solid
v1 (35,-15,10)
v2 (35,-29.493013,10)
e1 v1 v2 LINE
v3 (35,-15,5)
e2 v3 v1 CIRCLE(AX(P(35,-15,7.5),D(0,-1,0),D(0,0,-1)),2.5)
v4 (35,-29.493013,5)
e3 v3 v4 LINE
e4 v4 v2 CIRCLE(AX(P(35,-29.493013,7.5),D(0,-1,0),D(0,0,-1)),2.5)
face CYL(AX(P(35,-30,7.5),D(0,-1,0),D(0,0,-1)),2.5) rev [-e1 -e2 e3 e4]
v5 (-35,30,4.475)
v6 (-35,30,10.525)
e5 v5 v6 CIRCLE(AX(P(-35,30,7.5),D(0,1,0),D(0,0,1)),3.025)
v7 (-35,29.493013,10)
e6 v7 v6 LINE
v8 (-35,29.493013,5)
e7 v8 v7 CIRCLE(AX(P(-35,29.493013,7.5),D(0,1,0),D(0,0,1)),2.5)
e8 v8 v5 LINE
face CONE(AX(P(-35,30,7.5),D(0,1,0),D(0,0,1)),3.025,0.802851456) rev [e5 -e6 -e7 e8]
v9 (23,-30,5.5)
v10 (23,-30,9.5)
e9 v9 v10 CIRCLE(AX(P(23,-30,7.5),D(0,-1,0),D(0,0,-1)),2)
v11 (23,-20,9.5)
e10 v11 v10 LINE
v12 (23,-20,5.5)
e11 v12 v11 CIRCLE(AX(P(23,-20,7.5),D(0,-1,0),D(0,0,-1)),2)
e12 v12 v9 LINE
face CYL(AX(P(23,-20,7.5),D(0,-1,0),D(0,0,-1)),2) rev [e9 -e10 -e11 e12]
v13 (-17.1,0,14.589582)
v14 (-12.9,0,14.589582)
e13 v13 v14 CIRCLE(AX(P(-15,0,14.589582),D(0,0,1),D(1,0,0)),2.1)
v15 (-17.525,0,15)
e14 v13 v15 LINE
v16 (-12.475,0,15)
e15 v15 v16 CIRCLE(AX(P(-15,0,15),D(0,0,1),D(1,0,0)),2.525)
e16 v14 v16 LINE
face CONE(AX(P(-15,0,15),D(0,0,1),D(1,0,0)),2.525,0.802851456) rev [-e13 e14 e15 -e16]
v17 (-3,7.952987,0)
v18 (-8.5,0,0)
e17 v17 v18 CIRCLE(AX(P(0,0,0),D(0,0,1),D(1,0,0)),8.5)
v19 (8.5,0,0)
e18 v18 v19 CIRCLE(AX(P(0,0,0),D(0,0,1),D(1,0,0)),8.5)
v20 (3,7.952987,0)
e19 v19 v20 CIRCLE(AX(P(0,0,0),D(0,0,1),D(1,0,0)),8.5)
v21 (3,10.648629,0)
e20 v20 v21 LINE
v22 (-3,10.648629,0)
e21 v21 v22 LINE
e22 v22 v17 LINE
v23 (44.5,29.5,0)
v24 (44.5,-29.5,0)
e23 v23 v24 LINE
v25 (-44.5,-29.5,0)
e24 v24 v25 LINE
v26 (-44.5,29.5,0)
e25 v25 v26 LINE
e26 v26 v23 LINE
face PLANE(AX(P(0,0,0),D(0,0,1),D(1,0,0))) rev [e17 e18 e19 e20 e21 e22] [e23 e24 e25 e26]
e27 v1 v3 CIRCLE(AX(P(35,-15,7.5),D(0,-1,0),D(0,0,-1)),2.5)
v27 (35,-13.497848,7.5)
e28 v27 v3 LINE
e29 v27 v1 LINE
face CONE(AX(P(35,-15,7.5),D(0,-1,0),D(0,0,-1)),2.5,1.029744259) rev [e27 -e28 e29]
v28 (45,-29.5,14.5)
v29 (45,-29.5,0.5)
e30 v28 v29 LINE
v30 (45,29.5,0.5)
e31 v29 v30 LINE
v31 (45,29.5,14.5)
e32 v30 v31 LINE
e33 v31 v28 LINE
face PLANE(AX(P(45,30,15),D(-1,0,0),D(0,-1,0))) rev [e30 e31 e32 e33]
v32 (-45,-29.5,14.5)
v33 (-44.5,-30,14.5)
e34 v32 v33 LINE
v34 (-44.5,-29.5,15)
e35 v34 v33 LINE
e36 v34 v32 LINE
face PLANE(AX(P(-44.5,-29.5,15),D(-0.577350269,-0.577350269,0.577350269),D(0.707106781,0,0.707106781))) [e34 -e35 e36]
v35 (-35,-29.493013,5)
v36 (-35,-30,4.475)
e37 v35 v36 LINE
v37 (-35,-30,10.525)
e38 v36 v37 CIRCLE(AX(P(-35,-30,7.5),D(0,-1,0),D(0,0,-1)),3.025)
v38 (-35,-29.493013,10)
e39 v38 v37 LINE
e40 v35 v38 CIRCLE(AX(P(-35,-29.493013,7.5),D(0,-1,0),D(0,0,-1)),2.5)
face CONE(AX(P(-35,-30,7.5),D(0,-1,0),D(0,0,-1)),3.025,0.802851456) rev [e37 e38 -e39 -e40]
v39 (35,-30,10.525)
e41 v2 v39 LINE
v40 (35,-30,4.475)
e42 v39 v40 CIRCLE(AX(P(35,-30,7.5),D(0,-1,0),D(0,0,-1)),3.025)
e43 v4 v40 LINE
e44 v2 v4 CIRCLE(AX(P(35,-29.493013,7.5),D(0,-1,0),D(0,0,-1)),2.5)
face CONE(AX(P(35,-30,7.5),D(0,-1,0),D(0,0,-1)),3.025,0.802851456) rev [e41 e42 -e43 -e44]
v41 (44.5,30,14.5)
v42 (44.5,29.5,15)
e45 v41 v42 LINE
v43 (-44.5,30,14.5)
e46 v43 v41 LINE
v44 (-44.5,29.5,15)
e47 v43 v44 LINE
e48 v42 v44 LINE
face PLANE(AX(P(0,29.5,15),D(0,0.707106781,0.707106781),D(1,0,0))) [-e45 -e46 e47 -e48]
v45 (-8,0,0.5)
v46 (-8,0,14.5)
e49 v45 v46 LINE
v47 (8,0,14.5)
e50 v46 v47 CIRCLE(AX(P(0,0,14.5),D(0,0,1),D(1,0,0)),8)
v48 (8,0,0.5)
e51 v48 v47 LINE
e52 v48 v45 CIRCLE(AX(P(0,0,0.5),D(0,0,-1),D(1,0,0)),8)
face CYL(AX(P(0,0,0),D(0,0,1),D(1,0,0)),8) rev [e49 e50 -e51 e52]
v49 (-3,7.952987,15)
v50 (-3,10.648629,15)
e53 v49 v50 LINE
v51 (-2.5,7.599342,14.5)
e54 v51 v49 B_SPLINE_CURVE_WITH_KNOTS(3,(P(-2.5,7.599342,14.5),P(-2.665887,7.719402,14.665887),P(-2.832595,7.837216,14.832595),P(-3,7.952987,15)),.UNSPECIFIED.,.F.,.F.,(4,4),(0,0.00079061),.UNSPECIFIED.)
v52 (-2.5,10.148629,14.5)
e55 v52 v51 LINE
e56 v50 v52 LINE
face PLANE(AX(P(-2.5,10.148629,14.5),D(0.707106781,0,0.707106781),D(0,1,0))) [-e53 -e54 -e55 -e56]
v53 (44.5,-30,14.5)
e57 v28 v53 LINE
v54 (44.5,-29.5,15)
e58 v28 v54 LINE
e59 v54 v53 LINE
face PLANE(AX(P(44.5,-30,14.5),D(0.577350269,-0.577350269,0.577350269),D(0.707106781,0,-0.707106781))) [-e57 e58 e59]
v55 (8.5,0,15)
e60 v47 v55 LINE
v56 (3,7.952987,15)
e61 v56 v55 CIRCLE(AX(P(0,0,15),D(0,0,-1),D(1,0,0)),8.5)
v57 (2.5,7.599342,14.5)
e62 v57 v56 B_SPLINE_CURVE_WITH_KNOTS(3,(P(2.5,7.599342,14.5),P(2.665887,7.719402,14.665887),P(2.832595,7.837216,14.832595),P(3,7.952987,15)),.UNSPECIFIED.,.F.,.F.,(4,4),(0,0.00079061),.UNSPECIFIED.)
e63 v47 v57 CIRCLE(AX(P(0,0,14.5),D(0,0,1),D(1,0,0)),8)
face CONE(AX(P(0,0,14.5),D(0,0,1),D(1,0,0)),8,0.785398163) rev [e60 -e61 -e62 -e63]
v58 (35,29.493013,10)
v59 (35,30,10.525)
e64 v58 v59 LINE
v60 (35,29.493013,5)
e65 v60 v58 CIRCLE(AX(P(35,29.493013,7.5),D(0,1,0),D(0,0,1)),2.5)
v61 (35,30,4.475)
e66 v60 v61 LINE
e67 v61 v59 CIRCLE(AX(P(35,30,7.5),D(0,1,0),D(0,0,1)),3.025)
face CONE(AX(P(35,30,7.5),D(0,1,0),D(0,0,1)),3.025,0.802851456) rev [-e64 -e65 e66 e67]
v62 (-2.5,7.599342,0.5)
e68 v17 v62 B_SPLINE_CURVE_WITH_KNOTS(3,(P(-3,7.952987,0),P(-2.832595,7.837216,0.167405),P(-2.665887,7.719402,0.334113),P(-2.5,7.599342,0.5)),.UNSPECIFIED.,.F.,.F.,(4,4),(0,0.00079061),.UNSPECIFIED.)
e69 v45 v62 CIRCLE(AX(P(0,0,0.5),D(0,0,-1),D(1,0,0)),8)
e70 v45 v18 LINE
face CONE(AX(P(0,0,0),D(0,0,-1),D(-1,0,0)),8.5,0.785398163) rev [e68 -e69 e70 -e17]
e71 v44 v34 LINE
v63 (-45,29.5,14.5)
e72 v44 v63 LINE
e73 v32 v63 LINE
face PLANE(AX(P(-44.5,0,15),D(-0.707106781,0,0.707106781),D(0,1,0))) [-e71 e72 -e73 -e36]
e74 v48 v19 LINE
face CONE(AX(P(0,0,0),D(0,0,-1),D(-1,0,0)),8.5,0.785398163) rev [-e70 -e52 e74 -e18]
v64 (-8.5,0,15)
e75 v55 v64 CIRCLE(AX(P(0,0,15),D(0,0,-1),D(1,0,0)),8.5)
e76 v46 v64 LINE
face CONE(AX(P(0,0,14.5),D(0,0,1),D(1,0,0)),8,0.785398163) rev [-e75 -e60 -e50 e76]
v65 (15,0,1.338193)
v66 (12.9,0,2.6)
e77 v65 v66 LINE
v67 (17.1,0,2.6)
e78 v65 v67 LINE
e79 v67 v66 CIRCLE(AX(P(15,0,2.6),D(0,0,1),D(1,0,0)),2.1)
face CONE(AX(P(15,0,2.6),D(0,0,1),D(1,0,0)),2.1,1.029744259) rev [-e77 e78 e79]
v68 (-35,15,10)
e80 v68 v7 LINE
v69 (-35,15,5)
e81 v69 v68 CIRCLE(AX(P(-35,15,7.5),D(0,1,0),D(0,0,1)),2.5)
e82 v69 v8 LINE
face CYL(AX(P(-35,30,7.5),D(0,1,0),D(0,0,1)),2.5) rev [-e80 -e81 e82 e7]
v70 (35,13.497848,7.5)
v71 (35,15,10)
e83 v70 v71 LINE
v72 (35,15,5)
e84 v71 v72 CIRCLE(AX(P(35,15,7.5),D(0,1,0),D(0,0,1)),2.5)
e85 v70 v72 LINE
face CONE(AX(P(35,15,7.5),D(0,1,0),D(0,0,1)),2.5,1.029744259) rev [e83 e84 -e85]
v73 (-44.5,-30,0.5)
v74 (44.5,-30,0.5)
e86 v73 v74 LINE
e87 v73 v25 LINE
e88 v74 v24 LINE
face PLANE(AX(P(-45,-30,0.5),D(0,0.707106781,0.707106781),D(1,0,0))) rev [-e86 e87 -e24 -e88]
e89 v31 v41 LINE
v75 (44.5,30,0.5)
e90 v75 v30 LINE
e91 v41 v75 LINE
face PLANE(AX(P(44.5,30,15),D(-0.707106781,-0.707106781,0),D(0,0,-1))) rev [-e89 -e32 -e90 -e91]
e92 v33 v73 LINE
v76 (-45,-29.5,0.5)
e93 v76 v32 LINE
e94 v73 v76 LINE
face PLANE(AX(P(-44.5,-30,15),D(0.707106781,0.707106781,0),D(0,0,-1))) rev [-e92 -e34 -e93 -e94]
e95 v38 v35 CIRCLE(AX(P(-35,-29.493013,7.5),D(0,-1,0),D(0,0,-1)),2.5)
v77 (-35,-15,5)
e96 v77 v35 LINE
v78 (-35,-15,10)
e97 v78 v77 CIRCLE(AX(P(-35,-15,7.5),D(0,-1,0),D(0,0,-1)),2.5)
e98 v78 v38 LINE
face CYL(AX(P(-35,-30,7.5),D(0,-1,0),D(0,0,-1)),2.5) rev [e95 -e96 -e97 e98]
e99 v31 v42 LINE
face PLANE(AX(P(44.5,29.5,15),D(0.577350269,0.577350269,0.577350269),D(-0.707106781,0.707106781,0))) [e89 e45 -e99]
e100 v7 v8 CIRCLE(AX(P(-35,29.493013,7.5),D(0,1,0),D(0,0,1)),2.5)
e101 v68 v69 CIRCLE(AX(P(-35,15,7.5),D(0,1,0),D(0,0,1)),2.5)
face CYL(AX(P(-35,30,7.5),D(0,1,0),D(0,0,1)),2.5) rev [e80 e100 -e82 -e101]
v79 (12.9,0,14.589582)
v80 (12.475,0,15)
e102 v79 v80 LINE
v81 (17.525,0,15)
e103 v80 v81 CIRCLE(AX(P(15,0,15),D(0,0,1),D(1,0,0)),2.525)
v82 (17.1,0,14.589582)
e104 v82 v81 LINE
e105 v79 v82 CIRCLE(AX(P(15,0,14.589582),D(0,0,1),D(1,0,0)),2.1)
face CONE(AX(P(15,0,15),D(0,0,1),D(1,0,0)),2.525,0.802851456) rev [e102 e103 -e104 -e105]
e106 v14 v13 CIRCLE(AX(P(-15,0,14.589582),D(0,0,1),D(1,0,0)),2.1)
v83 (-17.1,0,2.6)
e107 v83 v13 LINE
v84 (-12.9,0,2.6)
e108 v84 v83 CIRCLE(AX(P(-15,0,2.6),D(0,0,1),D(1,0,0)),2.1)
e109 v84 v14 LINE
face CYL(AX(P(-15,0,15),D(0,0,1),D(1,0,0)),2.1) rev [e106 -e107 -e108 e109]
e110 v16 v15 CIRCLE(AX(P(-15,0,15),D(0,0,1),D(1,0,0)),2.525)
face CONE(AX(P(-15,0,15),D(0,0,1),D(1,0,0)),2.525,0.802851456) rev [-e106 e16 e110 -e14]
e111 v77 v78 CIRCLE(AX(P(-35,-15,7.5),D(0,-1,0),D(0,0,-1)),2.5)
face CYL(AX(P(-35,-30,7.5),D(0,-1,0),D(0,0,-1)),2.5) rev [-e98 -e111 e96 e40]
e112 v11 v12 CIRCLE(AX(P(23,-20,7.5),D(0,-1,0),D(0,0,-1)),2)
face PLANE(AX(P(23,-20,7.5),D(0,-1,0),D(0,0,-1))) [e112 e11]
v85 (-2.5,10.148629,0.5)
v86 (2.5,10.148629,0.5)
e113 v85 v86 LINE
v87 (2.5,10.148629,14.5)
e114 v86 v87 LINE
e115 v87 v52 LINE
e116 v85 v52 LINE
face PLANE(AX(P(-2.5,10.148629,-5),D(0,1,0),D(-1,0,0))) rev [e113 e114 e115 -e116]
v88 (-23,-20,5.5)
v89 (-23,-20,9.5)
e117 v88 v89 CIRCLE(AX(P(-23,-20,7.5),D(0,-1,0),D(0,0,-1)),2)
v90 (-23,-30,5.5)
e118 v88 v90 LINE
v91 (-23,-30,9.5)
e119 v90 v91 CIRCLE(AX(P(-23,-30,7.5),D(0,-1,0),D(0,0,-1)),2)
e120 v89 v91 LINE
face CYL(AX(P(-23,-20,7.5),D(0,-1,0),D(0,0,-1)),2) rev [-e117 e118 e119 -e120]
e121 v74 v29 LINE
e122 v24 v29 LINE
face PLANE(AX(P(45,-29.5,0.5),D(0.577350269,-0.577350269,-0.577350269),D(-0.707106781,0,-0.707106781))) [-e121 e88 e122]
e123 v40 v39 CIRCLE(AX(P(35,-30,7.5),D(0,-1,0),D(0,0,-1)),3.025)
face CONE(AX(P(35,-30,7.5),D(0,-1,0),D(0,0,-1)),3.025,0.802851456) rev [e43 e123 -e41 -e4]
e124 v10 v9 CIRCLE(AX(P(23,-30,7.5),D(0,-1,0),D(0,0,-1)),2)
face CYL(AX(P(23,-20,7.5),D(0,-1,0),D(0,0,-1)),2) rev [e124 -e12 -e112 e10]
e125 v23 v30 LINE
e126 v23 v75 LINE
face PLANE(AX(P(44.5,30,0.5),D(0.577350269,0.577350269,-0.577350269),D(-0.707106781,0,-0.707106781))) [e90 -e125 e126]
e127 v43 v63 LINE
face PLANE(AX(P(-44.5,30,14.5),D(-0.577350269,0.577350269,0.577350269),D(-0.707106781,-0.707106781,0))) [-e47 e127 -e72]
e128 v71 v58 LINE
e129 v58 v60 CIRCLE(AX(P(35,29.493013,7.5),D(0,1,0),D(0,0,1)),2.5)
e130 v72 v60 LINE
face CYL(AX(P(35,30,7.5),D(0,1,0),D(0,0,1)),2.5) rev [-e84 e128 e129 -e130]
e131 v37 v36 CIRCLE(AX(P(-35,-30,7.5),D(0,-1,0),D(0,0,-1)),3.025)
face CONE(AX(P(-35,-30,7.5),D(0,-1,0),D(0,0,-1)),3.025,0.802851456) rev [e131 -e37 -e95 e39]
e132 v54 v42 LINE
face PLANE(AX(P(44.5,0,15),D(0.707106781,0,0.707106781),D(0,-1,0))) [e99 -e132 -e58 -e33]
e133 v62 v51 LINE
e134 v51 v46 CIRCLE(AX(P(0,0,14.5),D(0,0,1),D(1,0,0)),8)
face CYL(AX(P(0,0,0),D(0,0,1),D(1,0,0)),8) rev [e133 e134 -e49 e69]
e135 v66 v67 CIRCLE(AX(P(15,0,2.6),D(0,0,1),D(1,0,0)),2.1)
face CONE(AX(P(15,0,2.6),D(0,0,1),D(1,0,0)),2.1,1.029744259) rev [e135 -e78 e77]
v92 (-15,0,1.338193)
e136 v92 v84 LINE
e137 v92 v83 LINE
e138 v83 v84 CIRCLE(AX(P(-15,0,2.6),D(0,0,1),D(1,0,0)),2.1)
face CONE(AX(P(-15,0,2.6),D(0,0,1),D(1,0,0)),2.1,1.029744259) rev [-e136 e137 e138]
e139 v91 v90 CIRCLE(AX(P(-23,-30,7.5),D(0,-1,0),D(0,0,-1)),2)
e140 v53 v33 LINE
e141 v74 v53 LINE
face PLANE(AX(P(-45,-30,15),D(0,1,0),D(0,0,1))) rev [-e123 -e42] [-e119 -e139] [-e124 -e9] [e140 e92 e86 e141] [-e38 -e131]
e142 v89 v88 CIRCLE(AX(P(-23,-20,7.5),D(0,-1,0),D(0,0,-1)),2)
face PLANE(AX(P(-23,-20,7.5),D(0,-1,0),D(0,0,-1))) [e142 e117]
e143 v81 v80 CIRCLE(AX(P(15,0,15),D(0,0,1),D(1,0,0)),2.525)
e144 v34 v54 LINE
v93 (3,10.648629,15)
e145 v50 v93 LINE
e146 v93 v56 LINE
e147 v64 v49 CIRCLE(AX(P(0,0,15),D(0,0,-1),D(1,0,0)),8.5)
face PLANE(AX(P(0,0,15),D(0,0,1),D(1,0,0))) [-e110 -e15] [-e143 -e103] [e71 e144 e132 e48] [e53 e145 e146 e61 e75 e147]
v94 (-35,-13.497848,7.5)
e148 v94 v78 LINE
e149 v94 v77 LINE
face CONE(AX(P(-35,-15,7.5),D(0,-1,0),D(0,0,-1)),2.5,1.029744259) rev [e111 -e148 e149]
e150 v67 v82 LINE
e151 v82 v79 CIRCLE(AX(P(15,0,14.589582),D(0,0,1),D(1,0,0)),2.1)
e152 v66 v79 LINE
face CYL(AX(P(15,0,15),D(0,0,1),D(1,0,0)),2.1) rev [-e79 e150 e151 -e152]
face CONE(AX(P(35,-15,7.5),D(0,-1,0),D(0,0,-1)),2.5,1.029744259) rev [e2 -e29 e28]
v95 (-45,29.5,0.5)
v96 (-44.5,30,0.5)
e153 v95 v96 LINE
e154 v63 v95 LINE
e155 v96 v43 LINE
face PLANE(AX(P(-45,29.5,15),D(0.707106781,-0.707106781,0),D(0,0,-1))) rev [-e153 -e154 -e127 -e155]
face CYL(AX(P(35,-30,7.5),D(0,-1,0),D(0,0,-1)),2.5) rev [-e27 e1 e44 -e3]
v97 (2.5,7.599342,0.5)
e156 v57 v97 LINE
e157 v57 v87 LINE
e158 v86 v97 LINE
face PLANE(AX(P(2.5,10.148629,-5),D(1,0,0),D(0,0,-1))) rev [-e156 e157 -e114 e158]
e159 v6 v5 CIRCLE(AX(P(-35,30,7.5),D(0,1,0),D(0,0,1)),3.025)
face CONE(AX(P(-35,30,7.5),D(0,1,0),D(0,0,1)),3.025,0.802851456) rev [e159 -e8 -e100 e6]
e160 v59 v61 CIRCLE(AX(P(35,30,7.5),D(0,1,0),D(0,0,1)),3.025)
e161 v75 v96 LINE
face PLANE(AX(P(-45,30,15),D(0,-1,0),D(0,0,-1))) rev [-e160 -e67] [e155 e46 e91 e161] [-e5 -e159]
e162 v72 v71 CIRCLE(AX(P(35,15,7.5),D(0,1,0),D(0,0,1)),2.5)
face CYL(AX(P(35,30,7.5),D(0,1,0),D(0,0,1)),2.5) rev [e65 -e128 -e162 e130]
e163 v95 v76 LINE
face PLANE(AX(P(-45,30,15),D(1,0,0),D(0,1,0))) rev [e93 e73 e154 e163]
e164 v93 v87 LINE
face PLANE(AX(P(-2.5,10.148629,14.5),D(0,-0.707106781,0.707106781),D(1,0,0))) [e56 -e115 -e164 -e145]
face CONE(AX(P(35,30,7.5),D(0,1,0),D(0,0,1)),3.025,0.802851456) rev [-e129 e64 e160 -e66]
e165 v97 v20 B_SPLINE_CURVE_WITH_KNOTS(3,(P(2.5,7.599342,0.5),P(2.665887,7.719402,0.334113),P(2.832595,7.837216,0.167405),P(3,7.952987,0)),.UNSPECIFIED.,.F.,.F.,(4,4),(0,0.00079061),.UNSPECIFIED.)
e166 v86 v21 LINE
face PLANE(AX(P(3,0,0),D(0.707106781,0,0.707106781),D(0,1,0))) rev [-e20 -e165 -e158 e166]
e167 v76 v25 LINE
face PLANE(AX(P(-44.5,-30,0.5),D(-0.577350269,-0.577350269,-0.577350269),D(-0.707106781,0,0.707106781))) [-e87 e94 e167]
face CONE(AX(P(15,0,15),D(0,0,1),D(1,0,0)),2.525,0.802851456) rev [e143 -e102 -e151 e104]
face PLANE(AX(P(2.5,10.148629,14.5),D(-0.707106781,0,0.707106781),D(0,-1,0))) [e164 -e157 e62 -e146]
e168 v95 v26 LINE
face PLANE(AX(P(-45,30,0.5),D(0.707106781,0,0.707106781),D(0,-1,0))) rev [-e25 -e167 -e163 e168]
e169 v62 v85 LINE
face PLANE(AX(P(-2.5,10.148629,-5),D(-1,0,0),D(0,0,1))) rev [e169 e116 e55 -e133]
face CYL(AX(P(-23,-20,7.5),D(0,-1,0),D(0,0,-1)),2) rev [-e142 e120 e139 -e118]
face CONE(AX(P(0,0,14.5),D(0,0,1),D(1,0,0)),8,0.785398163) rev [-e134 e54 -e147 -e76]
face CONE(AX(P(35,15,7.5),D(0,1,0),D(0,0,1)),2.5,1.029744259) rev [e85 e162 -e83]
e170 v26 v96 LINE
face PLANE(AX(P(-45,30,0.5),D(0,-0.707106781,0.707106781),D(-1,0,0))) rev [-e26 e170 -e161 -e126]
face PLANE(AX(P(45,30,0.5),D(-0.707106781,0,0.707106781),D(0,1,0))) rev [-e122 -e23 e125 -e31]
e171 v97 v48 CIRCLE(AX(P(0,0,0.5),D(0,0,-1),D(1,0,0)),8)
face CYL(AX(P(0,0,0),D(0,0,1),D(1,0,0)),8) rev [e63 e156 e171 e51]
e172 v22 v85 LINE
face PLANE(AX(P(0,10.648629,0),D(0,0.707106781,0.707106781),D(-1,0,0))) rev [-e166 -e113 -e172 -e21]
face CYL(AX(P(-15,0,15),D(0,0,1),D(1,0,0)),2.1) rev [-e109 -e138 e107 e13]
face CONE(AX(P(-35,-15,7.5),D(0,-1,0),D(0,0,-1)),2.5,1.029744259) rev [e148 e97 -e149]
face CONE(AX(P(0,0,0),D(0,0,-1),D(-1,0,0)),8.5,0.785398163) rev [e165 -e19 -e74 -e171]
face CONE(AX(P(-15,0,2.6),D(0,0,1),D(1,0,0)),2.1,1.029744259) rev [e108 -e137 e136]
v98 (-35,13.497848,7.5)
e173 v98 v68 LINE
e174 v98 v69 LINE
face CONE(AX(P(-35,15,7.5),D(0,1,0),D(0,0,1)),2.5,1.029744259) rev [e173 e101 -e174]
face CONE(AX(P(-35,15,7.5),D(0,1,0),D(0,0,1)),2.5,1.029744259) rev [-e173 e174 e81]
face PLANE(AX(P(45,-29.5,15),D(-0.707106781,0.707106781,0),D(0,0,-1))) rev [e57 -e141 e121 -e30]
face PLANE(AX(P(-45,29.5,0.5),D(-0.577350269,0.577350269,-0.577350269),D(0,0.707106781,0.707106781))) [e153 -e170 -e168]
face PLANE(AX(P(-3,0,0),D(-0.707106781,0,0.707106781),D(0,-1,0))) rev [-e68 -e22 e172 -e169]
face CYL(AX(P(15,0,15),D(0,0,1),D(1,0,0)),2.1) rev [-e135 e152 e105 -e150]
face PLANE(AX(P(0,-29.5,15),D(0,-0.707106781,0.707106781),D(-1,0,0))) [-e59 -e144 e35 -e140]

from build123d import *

# Parameters (mm, degrees)
SKETCH_1_W                   = 90
SKETCH_1_H                   = 60
EXTRUDE_1_DEPTH              = 15
SKETCH_3_R                   = 8
CUT_EXTRUDE_1_DEPTH          = 57.124860802
SKETCH_4_W                   = 5
SKETCH_4_H                   = 5.148629024
CUT_EXTRUDE_2_DEPTH          = 20
HOLE_WIZARD_M5_1_D           = 4.2
HOLE_WIZARD_M5_1_DEPTH       = 12.4
HOLE_WIZARD_M5_1_CSINK_D     = 5.05
HOLE_WIZARD_M5_1_CSINK_ANGLE = 92
HOLE_WIZARD_M5_1_TIP         = 1.2618073
SKETCH_8_R                   = 2
CUT_EXTRUDE_4_DEPTH          = 10
HOLE_WIZARD_M6_1_D           = 5
HOLE_WIZARD_M6_1_DEPTH       = 15
HOLE_WIZARD_M6_1_CSINK_D     = 6.05
HOLE_WIZARD_M6_1_CSINK_ANGLE = 92
HOLE_WIZARD_M6_1_TIP         = 1.502151548
HOLE_WIZARD_M6_2_D           = 5
HOLE_WIZARD_M6_2_DEPTH       = 15
HOLE_WIZARD_M6_2_CSINK_D     = 6.05
HOLE_WIZARD_M6_2_CSINK_ANGLE = 92
HOLE_WIZARD_M6_2_TIP         = 1.502151548
CHAMFER_2_SIZE               = 0.5
CHAMFER_3_SIZE               = 0.5


with BuildPart() as part:
    # 草图1 → 凸台-拉伸1 (new body)
    with BuildSketch(Plane.XY):
        Rectangle(SKETCH_1_W, SKETCH_1_H)
    extrude(amount=EXTRUDE_1_DEPTH)

    # 草图3 → 切除-拉伸1 (cut, through all)
    with BuildSketch(Plane.XY.offset(15)):
        Circle(SKETCH_3_R)
    extrude(amount=-CUT_EXTRUDE_1_DEPTH, mode=Mode.SUBTRACT)

    # 草图4 → 切除-拉伸2 (cut)
    with BuildSketch(Plane.XY.offset(15)):
        with Locations((0, 7.574314512)):
            Rectangle(SKETCH_4_W, SKETCH_4_H)
    extrude(amount=-CUT_EXTRUDE_2_DEPTH, mode=Mode.SUBTRACT)

    # M5 螺纹孔1
    with Locations(Plane.XY.offset(15)):
        with Locations((15, 0), (-15, 0)):
            CounterSinkHole(HOLE_WIZARD_M5_1_D / 2, HOLE_WIZARD_M5_1_CSINK_D / 2, depth=HOLE_WIZARD_M5_1_DEPTH, counter_sink_angle=HOLE_WIZARD_M5_1_CSINK_ANGLE)
            with Locations((0, 0, -(HOLE_WIZARD_M5_1_DEPTH + HOLE_WIZARD_M5_1_TIP / 2))):  # 118° drill point
                Cone(0, HOLE_WIZARD_M5_1_D / 2, HOLE_WIZARD_M5_1_TIP, mode=Mode.SUBTRACT)

    # 草图8 → 切除-拉伸4 (cut)
    with BuildSketch(Plane.XZ.offset(30)):
        with Locations(Location((-23, 7.5, 0), (0, 0, 270))):
            Circle(SKETCH_8_R)
        with Locations(Location((23, 7.5, 0), (0, 0, 270))):
            Circle(SKETCH_8_R)
    extrude(amount=-CUT_EXTRUDE_4_DEPTH, mode=Mode.SUBTRACT)

    # M6 螺纹孔1
    with Locations(Plane(origin=(0, 30, 0), x_dir=(1, 0, 0), z_dir=(0, 1, 0))):
        with Locations((-35, -7.5), (35, -7.5)):
            CounterSinkHole(HOLE_WIZARD_M6_1_D / 2, HOLE_WIZARD_M6_1_CSINK_D / 2, depth=HOLE_WIZARD_M6_1_DEPTH, counter_sink_angle=HOLE_WIZARD_M6_1_CSINK_ANGLE)
            with Locations((0, 0, -(HOLE_WIZARD_M6_1_DEPTH + HOLE_WIZARD_M6_1_TIP / 2))):  # 118° drill point
                Cone(0, HOLE_WIZARD_M6_1_D / 2, HOLE_WIZARD_M6_1_TIP, mode=Mode.SUBTRACT)

    # M6 螺纹孔2
    with Locations(Plane(origin=(0, -30, 0), x_dir=(-1, 0, 0), z_dir=(0, -1, 0))):
        with Locations((35, -7.5), (-35, -7.5)):
            CounterSinkHole(HOLE_WIZARD_M6_2_D / 2, HOLE_WIZARD_M6_2_CSINK_D / 2, depth=HOLE_WIZARD_M6_2_DEPTH, counter_sink_angle=HOLE_WIZARD_M6_2_CSINK_ANGLE)
            with Locations((0, 0, -(HOLE_WIZARD_M6_2_DEPTH + HOLE_WIZARD_M6_2_TIP / 2))):  # 118° drill point
                Cone(0, HOLE_WIZARD_M6_2_D / 2, HOLE_WIZARD_M6_2_TIP, mode=Mode.SUBTRACT)

    # 倒角2
    chamfer_2_edges = [part.edges().sort_by_distance(p)[0] for p in [
        (-45, 0, 15),
        (0, -30, 15),
        (45, 0, 15),
        (0, -30, 0),
        (-45, 0, 0),
        (0, 30, 0),
        (45, 0, 0),
        (0, 30, 15),
        (45, -30, 7.5),
        (-45, -30, 7.5),
        (-45, 30, 7.5),
        (45, 30, 7.5),
    ]]
    chamfer(chamfer_2_edges, length=CHAMFER_2_SIZE)

    # 倒角3
    chamfer_3_edges = [part.edges().sort_by_distance(p)[0] for p in [
        (0, -8, 0),
        (0, -8, 15),
        (0, 10.148629024, 0),
        (-2.5, 8.87398555, 0),
        (2.5, 8.87398555, 0),
        (-2.5, 8.87398555, 15),
        (2.5, 8.87398555, 15),
        (0, 10.148629024, 15),
    ]]
    chamfer(chamfer_3_edges, length=CHAMFER_3_SIZE)


solid = part.part
